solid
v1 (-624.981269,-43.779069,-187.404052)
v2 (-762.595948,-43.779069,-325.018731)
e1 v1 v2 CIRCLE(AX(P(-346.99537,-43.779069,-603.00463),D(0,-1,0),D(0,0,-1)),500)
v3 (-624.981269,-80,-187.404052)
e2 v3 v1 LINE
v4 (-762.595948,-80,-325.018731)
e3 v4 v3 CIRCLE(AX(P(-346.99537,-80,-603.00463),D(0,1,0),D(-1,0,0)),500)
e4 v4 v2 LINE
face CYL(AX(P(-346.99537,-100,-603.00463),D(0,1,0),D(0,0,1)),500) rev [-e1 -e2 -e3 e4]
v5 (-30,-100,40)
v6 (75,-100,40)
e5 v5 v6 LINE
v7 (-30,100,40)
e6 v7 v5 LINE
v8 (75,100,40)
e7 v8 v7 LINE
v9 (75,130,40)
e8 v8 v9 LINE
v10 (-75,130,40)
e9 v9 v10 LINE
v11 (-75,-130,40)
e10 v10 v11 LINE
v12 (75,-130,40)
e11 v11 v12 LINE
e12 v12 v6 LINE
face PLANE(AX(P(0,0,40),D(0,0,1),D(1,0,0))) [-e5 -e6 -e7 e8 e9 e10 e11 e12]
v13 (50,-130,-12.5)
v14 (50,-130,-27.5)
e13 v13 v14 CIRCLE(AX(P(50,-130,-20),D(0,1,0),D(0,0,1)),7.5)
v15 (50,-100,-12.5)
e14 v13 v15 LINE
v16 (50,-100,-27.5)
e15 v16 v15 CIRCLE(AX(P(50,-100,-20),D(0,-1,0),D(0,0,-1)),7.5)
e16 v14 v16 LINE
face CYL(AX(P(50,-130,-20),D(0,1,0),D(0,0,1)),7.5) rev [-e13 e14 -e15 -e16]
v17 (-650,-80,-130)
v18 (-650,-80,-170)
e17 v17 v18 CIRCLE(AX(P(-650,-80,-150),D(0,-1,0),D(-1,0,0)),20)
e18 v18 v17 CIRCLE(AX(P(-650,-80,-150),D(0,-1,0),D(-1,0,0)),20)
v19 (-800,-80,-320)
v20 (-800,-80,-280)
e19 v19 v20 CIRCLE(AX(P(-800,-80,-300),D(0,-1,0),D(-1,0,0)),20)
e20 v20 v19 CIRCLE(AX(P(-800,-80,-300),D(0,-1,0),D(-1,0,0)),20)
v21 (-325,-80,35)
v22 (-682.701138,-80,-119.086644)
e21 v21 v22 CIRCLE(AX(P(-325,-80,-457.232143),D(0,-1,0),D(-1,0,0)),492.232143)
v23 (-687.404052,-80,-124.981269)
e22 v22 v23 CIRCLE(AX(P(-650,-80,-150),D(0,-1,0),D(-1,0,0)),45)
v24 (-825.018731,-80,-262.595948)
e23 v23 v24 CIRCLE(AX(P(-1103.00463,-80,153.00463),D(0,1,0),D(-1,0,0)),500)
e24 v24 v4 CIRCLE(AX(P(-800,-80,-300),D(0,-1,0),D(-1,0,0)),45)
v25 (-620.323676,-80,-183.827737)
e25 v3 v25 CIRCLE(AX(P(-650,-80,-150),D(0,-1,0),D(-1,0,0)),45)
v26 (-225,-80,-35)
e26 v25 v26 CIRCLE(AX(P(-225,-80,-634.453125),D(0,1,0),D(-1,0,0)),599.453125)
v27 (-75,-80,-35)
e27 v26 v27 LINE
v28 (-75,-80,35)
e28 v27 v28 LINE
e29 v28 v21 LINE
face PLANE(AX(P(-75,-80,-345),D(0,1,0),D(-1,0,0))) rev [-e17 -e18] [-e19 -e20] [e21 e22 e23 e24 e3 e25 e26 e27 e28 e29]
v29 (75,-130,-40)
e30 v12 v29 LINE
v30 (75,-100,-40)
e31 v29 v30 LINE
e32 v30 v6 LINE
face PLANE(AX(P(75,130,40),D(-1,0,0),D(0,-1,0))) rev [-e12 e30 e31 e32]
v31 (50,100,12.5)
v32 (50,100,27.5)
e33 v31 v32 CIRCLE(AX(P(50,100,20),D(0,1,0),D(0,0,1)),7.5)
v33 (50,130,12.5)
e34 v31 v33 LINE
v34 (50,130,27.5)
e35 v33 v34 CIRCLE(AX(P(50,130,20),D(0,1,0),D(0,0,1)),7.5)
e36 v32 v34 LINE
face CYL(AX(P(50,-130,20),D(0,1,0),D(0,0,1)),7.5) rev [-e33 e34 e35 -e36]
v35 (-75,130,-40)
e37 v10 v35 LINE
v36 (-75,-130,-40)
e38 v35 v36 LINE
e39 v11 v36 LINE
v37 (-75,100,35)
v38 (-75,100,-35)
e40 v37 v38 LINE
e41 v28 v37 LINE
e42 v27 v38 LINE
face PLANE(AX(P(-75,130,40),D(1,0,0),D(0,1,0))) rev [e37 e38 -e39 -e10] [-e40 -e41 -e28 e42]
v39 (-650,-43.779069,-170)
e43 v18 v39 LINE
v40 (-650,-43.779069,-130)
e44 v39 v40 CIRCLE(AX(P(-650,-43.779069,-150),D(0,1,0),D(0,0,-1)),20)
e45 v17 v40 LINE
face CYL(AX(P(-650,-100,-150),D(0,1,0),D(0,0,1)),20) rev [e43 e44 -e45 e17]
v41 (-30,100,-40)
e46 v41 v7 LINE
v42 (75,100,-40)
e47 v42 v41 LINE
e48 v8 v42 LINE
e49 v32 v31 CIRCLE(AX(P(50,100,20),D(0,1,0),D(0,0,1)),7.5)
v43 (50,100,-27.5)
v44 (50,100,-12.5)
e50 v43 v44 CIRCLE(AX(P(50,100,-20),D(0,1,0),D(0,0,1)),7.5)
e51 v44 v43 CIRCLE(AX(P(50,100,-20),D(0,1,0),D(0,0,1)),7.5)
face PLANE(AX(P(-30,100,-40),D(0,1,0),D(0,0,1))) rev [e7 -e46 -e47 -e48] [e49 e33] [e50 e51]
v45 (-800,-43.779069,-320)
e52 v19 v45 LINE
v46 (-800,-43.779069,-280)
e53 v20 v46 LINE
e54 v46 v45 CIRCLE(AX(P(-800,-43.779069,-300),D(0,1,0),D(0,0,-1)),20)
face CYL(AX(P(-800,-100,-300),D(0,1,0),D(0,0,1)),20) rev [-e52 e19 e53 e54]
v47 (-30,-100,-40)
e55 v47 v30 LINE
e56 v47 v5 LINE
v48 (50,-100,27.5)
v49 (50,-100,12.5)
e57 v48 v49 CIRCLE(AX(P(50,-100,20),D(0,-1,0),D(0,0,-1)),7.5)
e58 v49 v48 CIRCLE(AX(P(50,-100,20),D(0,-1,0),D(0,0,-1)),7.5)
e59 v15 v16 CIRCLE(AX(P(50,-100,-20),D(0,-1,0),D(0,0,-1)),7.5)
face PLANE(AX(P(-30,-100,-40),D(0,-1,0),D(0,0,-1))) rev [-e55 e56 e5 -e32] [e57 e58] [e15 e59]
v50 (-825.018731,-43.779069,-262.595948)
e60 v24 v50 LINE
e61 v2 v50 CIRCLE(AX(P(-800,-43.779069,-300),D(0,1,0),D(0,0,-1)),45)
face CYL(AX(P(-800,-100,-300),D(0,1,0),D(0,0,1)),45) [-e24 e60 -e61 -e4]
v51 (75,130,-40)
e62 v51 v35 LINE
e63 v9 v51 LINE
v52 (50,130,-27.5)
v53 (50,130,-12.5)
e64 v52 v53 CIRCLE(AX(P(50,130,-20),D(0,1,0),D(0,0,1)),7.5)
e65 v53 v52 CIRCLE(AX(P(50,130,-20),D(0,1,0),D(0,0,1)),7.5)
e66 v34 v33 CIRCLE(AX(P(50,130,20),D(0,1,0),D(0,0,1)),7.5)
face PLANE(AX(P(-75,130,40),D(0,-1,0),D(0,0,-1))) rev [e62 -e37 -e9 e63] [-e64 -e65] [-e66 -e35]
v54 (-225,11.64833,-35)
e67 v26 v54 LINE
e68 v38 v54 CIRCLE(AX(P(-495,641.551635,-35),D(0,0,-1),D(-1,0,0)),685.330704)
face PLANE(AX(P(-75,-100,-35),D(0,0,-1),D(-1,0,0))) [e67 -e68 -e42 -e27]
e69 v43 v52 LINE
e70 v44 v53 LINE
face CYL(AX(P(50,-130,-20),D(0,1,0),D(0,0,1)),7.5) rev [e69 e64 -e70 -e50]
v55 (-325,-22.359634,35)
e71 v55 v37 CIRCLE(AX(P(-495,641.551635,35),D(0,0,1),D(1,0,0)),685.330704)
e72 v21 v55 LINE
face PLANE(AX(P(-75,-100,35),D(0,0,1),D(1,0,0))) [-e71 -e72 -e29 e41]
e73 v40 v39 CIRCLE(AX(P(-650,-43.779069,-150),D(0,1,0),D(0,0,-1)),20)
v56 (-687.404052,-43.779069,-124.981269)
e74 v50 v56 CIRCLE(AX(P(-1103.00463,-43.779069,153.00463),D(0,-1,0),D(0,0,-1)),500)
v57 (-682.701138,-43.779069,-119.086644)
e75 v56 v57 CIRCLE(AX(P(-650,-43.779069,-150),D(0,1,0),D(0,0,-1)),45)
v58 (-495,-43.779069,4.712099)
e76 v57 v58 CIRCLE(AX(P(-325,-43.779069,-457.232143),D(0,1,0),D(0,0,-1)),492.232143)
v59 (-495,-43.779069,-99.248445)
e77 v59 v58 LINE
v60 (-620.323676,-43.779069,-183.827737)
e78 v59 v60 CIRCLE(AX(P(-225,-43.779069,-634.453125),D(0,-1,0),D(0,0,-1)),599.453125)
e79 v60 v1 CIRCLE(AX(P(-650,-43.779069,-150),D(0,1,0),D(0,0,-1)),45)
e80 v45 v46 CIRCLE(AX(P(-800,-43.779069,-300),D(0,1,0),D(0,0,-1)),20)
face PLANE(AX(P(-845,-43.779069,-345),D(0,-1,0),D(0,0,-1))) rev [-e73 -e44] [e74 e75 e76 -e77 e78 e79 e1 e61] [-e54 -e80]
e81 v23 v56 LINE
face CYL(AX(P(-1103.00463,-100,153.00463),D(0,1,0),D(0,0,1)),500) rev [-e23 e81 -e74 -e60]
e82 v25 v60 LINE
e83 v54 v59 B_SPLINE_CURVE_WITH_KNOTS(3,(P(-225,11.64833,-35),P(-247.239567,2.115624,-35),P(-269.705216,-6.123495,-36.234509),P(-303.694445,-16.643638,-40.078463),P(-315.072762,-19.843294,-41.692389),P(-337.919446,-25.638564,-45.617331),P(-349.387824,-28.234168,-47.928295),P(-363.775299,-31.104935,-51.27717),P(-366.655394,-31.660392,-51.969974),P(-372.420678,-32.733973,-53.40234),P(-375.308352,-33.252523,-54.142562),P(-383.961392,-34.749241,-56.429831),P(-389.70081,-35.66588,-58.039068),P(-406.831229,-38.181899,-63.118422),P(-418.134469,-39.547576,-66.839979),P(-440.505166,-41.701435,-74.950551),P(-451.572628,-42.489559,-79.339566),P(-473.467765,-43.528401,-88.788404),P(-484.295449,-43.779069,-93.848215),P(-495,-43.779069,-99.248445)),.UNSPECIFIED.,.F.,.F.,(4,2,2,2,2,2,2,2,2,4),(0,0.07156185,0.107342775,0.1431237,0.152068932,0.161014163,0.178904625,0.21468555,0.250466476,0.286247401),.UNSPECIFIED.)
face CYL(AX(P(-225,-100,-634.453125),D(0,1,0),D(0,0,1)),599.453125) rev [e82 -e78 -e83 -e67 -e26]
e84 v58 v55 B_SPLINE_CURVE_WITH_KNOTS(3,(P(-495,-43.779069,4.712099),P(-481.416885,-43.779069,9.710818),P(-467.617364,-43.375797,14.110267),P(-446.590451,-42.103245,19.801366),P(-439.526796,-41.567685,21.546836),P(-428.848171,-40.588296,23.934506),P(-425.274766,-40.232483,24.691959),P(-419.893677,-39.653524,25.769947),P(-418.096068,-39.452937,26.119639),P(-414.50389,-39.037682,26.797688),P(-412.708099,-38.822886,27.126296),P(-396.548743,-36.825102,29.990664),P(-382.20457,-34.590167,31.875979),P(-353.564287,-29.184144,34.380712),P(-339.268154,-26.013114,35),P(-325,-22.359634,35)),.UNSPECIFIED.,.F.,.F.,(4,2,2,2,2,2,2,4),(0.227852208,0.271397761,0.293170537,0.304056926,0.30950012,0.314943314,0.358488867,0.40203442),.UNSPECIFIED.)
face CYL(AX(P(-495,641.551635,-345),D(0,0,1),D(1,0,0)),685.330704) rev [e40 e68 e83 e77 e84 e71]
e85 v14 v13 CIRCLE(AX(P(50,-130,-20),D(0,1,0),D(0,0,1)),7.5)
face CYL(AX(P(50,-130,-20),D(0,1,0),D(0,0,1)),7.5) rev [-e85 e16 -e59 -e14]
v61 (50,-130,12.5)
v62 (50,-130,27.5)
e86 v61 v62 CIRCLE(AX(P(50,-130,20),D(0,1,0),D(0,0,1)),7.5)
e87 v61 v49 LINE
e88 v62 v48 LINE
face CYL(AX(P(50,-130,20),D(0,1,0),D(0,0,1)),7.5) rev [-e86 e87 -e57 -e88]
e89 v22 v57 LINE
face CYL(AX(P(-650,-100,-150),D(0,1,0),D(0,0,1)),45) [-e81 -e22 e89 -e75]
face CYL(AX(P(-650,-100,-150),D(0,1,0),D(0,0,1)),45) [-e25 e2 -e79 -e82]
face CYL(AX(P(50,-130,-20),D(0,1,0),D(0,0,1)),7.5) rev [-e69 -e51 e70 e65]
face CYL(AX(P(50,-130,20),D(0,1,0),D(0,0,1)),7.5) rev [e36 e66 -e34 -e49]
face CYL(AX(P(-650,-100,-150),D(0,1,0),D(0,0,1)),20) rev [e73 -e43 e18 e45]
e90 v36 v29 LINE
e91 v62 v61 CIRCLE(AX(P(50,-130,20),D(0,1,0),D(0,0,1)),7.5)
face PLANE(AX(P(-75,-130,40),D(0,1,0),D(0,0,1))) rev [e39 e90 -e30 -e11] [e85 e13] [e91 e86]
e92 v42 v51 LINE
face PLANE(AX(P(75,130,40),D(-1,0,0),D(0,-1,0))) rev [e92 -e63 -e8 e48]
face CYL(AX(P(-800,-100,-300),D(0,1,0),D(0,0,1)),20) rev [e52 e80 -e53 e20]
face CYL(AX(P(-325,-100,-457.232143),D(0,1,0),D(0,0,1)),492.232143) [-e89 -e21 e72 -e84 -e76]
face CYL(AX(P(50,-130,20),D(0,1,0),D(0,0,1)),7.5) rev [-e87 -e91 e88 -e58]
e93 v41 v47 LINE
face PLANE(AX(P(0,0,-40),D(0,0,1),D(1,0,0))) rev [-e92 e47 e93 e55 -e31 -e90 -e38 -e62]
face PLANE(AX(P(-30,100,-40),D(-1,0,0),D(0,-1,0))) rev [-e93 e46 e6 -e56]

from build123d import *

# Parameters (mm, degrees)
SKETCH1_W           = 150
SKETCH1_H           = 260
BOSS_EXTRUDE1_DEPTH = 40
SKETCH2_W           = 210
SKETCH2_H           = 200
CUT_EXTRUDE1_DEPTH  = 171.073513517
SKETCH3_R           = 20
BOSS_EXTRUDE2_DEPTH = 100
SKETCH4_W           = 803.619965953
SKETCH4_H           = 20
CUT_EXTRUDE2_DEPTH  = 938.629990988
SKETCH5_R           = 7.5
CUT_EXTRUDE3_DEPTH  = 950.025816298


with BuildPart() as part:
    # Sketch1 → Boss-Extrude1 (new, symmetric)
    with BuildSketch(Plane.XY):
        Rectangle(SKETCH1_W, SKETCH1_H)
    extrude(amount=BOSS_EXTRUDE1_DEPTH, both=True)

    # Sketch2 → Cut-Extrude1 (cut, through all)
    with BuildSketch(Plane.XY.offset(40)):
        with Locations((75, 0)):
            Rectangle(SKETCH2_W, SKETCH2_H)
    extrude(amount=-CUT_EXTRUDE1_DEPTH, mode=Mode.SUBTRACT)

    # Sketch3 → Boss-Extrude2 (add, symmetric)
    with BuildSketch(Plane(origin=(0, 0, 0), x_dir=(1, 0, 0), z_dir=(0, 1, 0))):
        with BuildLine():
            Line((-75, 35), (-75, -35))
            Line((-75, -35), (-325, -35))
            ThreePointArc((-325, -35), (-519.738798114, 5.159932949), (-682.701137952, 119.086644041))
            ThreePointArc((-682.701137952, 119.086644041), (-685.176285552, 121.935272409), (-687.404051985, 124.981269115))
            ThreePointArc((-687.404051985, 124.981269115), (-749.451239008, 200.548760992), (-825.018730885, 262.595948015))
            ThreePointArc((-825.018730885, 262.595948015), (-831.819805153, 331.819805153), (-762.595948015, 325.018730885))
            ThreePointArc((-762.595948015, 325.018730885), (-700.548760992, 249.451239008), (-624.981269115, 187.404051985))
            ThreePointArc((-624.981269115, 187.404051985), (-622.594074072, 185.691949008), (-620.323675597, 183.827736695))
            ThreePointArc((-620.323675597, 183.827736695), (-436.205174947, 73.439379047), (-225, 35))
            Line((-225, 35), (-75, 35))
        make_face()
        with Locations(Location((-800, 300, 0), (0, 0, 270))):
            Circle(SKETCH3_R, mode=Mode.SUBTRACT)
        with Locations(Location((-650, 150, 0), (0, 0, 270))):
            Circle(SKETCH3_R, mode=Mode.SUBTRACT)
    extrude(amount=BOSS_EXTRUDE2_DEPTH, both=True)

    # Sketch4 → Cut-Extrude2 (cut, through all)
    with BuildSketch(Plane.XY.offset(40)):
        with BuildLine():
            Line((-845, -43.779068644), (-495, -43.779068644))
            ThreePointArc((-495, -43.779068644), (-273.03580211, -6.838732152), (-75, 100))
            Line((-75, 100), (-75, 271.543377567))
            Line((-75, 271.543377567), (-940.801447503, 271.543377567))
            Line((-940.801447503, 271.543377567), (-972.091183845, -20.942543752))
            Line((-972.091183845, -20.942543752), (-845, -43.779068644))
        make_face()
        with Locations((-476.809982977, -90)):
            Rectangle(SKETCH4_W, SKETCH4_H)
    extrude(amount=-CUT_EXTRUDE2_DEPTH, mode=Mode.SUBTRACT)

    # Sketch5 → Cut-Extrude3 (cut, through all)
    with BuildSketch(Plane(origin=(0, 130, 0), x_dir=(1, 0, 0), z_dir=(0, 1, 0))):
        with Locations(Location((50, 20, 0), (0, 0, 270))):
            Circle(SKETCH5_R)
        with Locations(Location((50, -20, 0), (0, 0, 270))):
            Circle(SKETCH5_R)
    extrude(amount=-CUT_EXTRUDE3_DEPTH, mode=Mode.SUBTRACT)


solid = part.part
